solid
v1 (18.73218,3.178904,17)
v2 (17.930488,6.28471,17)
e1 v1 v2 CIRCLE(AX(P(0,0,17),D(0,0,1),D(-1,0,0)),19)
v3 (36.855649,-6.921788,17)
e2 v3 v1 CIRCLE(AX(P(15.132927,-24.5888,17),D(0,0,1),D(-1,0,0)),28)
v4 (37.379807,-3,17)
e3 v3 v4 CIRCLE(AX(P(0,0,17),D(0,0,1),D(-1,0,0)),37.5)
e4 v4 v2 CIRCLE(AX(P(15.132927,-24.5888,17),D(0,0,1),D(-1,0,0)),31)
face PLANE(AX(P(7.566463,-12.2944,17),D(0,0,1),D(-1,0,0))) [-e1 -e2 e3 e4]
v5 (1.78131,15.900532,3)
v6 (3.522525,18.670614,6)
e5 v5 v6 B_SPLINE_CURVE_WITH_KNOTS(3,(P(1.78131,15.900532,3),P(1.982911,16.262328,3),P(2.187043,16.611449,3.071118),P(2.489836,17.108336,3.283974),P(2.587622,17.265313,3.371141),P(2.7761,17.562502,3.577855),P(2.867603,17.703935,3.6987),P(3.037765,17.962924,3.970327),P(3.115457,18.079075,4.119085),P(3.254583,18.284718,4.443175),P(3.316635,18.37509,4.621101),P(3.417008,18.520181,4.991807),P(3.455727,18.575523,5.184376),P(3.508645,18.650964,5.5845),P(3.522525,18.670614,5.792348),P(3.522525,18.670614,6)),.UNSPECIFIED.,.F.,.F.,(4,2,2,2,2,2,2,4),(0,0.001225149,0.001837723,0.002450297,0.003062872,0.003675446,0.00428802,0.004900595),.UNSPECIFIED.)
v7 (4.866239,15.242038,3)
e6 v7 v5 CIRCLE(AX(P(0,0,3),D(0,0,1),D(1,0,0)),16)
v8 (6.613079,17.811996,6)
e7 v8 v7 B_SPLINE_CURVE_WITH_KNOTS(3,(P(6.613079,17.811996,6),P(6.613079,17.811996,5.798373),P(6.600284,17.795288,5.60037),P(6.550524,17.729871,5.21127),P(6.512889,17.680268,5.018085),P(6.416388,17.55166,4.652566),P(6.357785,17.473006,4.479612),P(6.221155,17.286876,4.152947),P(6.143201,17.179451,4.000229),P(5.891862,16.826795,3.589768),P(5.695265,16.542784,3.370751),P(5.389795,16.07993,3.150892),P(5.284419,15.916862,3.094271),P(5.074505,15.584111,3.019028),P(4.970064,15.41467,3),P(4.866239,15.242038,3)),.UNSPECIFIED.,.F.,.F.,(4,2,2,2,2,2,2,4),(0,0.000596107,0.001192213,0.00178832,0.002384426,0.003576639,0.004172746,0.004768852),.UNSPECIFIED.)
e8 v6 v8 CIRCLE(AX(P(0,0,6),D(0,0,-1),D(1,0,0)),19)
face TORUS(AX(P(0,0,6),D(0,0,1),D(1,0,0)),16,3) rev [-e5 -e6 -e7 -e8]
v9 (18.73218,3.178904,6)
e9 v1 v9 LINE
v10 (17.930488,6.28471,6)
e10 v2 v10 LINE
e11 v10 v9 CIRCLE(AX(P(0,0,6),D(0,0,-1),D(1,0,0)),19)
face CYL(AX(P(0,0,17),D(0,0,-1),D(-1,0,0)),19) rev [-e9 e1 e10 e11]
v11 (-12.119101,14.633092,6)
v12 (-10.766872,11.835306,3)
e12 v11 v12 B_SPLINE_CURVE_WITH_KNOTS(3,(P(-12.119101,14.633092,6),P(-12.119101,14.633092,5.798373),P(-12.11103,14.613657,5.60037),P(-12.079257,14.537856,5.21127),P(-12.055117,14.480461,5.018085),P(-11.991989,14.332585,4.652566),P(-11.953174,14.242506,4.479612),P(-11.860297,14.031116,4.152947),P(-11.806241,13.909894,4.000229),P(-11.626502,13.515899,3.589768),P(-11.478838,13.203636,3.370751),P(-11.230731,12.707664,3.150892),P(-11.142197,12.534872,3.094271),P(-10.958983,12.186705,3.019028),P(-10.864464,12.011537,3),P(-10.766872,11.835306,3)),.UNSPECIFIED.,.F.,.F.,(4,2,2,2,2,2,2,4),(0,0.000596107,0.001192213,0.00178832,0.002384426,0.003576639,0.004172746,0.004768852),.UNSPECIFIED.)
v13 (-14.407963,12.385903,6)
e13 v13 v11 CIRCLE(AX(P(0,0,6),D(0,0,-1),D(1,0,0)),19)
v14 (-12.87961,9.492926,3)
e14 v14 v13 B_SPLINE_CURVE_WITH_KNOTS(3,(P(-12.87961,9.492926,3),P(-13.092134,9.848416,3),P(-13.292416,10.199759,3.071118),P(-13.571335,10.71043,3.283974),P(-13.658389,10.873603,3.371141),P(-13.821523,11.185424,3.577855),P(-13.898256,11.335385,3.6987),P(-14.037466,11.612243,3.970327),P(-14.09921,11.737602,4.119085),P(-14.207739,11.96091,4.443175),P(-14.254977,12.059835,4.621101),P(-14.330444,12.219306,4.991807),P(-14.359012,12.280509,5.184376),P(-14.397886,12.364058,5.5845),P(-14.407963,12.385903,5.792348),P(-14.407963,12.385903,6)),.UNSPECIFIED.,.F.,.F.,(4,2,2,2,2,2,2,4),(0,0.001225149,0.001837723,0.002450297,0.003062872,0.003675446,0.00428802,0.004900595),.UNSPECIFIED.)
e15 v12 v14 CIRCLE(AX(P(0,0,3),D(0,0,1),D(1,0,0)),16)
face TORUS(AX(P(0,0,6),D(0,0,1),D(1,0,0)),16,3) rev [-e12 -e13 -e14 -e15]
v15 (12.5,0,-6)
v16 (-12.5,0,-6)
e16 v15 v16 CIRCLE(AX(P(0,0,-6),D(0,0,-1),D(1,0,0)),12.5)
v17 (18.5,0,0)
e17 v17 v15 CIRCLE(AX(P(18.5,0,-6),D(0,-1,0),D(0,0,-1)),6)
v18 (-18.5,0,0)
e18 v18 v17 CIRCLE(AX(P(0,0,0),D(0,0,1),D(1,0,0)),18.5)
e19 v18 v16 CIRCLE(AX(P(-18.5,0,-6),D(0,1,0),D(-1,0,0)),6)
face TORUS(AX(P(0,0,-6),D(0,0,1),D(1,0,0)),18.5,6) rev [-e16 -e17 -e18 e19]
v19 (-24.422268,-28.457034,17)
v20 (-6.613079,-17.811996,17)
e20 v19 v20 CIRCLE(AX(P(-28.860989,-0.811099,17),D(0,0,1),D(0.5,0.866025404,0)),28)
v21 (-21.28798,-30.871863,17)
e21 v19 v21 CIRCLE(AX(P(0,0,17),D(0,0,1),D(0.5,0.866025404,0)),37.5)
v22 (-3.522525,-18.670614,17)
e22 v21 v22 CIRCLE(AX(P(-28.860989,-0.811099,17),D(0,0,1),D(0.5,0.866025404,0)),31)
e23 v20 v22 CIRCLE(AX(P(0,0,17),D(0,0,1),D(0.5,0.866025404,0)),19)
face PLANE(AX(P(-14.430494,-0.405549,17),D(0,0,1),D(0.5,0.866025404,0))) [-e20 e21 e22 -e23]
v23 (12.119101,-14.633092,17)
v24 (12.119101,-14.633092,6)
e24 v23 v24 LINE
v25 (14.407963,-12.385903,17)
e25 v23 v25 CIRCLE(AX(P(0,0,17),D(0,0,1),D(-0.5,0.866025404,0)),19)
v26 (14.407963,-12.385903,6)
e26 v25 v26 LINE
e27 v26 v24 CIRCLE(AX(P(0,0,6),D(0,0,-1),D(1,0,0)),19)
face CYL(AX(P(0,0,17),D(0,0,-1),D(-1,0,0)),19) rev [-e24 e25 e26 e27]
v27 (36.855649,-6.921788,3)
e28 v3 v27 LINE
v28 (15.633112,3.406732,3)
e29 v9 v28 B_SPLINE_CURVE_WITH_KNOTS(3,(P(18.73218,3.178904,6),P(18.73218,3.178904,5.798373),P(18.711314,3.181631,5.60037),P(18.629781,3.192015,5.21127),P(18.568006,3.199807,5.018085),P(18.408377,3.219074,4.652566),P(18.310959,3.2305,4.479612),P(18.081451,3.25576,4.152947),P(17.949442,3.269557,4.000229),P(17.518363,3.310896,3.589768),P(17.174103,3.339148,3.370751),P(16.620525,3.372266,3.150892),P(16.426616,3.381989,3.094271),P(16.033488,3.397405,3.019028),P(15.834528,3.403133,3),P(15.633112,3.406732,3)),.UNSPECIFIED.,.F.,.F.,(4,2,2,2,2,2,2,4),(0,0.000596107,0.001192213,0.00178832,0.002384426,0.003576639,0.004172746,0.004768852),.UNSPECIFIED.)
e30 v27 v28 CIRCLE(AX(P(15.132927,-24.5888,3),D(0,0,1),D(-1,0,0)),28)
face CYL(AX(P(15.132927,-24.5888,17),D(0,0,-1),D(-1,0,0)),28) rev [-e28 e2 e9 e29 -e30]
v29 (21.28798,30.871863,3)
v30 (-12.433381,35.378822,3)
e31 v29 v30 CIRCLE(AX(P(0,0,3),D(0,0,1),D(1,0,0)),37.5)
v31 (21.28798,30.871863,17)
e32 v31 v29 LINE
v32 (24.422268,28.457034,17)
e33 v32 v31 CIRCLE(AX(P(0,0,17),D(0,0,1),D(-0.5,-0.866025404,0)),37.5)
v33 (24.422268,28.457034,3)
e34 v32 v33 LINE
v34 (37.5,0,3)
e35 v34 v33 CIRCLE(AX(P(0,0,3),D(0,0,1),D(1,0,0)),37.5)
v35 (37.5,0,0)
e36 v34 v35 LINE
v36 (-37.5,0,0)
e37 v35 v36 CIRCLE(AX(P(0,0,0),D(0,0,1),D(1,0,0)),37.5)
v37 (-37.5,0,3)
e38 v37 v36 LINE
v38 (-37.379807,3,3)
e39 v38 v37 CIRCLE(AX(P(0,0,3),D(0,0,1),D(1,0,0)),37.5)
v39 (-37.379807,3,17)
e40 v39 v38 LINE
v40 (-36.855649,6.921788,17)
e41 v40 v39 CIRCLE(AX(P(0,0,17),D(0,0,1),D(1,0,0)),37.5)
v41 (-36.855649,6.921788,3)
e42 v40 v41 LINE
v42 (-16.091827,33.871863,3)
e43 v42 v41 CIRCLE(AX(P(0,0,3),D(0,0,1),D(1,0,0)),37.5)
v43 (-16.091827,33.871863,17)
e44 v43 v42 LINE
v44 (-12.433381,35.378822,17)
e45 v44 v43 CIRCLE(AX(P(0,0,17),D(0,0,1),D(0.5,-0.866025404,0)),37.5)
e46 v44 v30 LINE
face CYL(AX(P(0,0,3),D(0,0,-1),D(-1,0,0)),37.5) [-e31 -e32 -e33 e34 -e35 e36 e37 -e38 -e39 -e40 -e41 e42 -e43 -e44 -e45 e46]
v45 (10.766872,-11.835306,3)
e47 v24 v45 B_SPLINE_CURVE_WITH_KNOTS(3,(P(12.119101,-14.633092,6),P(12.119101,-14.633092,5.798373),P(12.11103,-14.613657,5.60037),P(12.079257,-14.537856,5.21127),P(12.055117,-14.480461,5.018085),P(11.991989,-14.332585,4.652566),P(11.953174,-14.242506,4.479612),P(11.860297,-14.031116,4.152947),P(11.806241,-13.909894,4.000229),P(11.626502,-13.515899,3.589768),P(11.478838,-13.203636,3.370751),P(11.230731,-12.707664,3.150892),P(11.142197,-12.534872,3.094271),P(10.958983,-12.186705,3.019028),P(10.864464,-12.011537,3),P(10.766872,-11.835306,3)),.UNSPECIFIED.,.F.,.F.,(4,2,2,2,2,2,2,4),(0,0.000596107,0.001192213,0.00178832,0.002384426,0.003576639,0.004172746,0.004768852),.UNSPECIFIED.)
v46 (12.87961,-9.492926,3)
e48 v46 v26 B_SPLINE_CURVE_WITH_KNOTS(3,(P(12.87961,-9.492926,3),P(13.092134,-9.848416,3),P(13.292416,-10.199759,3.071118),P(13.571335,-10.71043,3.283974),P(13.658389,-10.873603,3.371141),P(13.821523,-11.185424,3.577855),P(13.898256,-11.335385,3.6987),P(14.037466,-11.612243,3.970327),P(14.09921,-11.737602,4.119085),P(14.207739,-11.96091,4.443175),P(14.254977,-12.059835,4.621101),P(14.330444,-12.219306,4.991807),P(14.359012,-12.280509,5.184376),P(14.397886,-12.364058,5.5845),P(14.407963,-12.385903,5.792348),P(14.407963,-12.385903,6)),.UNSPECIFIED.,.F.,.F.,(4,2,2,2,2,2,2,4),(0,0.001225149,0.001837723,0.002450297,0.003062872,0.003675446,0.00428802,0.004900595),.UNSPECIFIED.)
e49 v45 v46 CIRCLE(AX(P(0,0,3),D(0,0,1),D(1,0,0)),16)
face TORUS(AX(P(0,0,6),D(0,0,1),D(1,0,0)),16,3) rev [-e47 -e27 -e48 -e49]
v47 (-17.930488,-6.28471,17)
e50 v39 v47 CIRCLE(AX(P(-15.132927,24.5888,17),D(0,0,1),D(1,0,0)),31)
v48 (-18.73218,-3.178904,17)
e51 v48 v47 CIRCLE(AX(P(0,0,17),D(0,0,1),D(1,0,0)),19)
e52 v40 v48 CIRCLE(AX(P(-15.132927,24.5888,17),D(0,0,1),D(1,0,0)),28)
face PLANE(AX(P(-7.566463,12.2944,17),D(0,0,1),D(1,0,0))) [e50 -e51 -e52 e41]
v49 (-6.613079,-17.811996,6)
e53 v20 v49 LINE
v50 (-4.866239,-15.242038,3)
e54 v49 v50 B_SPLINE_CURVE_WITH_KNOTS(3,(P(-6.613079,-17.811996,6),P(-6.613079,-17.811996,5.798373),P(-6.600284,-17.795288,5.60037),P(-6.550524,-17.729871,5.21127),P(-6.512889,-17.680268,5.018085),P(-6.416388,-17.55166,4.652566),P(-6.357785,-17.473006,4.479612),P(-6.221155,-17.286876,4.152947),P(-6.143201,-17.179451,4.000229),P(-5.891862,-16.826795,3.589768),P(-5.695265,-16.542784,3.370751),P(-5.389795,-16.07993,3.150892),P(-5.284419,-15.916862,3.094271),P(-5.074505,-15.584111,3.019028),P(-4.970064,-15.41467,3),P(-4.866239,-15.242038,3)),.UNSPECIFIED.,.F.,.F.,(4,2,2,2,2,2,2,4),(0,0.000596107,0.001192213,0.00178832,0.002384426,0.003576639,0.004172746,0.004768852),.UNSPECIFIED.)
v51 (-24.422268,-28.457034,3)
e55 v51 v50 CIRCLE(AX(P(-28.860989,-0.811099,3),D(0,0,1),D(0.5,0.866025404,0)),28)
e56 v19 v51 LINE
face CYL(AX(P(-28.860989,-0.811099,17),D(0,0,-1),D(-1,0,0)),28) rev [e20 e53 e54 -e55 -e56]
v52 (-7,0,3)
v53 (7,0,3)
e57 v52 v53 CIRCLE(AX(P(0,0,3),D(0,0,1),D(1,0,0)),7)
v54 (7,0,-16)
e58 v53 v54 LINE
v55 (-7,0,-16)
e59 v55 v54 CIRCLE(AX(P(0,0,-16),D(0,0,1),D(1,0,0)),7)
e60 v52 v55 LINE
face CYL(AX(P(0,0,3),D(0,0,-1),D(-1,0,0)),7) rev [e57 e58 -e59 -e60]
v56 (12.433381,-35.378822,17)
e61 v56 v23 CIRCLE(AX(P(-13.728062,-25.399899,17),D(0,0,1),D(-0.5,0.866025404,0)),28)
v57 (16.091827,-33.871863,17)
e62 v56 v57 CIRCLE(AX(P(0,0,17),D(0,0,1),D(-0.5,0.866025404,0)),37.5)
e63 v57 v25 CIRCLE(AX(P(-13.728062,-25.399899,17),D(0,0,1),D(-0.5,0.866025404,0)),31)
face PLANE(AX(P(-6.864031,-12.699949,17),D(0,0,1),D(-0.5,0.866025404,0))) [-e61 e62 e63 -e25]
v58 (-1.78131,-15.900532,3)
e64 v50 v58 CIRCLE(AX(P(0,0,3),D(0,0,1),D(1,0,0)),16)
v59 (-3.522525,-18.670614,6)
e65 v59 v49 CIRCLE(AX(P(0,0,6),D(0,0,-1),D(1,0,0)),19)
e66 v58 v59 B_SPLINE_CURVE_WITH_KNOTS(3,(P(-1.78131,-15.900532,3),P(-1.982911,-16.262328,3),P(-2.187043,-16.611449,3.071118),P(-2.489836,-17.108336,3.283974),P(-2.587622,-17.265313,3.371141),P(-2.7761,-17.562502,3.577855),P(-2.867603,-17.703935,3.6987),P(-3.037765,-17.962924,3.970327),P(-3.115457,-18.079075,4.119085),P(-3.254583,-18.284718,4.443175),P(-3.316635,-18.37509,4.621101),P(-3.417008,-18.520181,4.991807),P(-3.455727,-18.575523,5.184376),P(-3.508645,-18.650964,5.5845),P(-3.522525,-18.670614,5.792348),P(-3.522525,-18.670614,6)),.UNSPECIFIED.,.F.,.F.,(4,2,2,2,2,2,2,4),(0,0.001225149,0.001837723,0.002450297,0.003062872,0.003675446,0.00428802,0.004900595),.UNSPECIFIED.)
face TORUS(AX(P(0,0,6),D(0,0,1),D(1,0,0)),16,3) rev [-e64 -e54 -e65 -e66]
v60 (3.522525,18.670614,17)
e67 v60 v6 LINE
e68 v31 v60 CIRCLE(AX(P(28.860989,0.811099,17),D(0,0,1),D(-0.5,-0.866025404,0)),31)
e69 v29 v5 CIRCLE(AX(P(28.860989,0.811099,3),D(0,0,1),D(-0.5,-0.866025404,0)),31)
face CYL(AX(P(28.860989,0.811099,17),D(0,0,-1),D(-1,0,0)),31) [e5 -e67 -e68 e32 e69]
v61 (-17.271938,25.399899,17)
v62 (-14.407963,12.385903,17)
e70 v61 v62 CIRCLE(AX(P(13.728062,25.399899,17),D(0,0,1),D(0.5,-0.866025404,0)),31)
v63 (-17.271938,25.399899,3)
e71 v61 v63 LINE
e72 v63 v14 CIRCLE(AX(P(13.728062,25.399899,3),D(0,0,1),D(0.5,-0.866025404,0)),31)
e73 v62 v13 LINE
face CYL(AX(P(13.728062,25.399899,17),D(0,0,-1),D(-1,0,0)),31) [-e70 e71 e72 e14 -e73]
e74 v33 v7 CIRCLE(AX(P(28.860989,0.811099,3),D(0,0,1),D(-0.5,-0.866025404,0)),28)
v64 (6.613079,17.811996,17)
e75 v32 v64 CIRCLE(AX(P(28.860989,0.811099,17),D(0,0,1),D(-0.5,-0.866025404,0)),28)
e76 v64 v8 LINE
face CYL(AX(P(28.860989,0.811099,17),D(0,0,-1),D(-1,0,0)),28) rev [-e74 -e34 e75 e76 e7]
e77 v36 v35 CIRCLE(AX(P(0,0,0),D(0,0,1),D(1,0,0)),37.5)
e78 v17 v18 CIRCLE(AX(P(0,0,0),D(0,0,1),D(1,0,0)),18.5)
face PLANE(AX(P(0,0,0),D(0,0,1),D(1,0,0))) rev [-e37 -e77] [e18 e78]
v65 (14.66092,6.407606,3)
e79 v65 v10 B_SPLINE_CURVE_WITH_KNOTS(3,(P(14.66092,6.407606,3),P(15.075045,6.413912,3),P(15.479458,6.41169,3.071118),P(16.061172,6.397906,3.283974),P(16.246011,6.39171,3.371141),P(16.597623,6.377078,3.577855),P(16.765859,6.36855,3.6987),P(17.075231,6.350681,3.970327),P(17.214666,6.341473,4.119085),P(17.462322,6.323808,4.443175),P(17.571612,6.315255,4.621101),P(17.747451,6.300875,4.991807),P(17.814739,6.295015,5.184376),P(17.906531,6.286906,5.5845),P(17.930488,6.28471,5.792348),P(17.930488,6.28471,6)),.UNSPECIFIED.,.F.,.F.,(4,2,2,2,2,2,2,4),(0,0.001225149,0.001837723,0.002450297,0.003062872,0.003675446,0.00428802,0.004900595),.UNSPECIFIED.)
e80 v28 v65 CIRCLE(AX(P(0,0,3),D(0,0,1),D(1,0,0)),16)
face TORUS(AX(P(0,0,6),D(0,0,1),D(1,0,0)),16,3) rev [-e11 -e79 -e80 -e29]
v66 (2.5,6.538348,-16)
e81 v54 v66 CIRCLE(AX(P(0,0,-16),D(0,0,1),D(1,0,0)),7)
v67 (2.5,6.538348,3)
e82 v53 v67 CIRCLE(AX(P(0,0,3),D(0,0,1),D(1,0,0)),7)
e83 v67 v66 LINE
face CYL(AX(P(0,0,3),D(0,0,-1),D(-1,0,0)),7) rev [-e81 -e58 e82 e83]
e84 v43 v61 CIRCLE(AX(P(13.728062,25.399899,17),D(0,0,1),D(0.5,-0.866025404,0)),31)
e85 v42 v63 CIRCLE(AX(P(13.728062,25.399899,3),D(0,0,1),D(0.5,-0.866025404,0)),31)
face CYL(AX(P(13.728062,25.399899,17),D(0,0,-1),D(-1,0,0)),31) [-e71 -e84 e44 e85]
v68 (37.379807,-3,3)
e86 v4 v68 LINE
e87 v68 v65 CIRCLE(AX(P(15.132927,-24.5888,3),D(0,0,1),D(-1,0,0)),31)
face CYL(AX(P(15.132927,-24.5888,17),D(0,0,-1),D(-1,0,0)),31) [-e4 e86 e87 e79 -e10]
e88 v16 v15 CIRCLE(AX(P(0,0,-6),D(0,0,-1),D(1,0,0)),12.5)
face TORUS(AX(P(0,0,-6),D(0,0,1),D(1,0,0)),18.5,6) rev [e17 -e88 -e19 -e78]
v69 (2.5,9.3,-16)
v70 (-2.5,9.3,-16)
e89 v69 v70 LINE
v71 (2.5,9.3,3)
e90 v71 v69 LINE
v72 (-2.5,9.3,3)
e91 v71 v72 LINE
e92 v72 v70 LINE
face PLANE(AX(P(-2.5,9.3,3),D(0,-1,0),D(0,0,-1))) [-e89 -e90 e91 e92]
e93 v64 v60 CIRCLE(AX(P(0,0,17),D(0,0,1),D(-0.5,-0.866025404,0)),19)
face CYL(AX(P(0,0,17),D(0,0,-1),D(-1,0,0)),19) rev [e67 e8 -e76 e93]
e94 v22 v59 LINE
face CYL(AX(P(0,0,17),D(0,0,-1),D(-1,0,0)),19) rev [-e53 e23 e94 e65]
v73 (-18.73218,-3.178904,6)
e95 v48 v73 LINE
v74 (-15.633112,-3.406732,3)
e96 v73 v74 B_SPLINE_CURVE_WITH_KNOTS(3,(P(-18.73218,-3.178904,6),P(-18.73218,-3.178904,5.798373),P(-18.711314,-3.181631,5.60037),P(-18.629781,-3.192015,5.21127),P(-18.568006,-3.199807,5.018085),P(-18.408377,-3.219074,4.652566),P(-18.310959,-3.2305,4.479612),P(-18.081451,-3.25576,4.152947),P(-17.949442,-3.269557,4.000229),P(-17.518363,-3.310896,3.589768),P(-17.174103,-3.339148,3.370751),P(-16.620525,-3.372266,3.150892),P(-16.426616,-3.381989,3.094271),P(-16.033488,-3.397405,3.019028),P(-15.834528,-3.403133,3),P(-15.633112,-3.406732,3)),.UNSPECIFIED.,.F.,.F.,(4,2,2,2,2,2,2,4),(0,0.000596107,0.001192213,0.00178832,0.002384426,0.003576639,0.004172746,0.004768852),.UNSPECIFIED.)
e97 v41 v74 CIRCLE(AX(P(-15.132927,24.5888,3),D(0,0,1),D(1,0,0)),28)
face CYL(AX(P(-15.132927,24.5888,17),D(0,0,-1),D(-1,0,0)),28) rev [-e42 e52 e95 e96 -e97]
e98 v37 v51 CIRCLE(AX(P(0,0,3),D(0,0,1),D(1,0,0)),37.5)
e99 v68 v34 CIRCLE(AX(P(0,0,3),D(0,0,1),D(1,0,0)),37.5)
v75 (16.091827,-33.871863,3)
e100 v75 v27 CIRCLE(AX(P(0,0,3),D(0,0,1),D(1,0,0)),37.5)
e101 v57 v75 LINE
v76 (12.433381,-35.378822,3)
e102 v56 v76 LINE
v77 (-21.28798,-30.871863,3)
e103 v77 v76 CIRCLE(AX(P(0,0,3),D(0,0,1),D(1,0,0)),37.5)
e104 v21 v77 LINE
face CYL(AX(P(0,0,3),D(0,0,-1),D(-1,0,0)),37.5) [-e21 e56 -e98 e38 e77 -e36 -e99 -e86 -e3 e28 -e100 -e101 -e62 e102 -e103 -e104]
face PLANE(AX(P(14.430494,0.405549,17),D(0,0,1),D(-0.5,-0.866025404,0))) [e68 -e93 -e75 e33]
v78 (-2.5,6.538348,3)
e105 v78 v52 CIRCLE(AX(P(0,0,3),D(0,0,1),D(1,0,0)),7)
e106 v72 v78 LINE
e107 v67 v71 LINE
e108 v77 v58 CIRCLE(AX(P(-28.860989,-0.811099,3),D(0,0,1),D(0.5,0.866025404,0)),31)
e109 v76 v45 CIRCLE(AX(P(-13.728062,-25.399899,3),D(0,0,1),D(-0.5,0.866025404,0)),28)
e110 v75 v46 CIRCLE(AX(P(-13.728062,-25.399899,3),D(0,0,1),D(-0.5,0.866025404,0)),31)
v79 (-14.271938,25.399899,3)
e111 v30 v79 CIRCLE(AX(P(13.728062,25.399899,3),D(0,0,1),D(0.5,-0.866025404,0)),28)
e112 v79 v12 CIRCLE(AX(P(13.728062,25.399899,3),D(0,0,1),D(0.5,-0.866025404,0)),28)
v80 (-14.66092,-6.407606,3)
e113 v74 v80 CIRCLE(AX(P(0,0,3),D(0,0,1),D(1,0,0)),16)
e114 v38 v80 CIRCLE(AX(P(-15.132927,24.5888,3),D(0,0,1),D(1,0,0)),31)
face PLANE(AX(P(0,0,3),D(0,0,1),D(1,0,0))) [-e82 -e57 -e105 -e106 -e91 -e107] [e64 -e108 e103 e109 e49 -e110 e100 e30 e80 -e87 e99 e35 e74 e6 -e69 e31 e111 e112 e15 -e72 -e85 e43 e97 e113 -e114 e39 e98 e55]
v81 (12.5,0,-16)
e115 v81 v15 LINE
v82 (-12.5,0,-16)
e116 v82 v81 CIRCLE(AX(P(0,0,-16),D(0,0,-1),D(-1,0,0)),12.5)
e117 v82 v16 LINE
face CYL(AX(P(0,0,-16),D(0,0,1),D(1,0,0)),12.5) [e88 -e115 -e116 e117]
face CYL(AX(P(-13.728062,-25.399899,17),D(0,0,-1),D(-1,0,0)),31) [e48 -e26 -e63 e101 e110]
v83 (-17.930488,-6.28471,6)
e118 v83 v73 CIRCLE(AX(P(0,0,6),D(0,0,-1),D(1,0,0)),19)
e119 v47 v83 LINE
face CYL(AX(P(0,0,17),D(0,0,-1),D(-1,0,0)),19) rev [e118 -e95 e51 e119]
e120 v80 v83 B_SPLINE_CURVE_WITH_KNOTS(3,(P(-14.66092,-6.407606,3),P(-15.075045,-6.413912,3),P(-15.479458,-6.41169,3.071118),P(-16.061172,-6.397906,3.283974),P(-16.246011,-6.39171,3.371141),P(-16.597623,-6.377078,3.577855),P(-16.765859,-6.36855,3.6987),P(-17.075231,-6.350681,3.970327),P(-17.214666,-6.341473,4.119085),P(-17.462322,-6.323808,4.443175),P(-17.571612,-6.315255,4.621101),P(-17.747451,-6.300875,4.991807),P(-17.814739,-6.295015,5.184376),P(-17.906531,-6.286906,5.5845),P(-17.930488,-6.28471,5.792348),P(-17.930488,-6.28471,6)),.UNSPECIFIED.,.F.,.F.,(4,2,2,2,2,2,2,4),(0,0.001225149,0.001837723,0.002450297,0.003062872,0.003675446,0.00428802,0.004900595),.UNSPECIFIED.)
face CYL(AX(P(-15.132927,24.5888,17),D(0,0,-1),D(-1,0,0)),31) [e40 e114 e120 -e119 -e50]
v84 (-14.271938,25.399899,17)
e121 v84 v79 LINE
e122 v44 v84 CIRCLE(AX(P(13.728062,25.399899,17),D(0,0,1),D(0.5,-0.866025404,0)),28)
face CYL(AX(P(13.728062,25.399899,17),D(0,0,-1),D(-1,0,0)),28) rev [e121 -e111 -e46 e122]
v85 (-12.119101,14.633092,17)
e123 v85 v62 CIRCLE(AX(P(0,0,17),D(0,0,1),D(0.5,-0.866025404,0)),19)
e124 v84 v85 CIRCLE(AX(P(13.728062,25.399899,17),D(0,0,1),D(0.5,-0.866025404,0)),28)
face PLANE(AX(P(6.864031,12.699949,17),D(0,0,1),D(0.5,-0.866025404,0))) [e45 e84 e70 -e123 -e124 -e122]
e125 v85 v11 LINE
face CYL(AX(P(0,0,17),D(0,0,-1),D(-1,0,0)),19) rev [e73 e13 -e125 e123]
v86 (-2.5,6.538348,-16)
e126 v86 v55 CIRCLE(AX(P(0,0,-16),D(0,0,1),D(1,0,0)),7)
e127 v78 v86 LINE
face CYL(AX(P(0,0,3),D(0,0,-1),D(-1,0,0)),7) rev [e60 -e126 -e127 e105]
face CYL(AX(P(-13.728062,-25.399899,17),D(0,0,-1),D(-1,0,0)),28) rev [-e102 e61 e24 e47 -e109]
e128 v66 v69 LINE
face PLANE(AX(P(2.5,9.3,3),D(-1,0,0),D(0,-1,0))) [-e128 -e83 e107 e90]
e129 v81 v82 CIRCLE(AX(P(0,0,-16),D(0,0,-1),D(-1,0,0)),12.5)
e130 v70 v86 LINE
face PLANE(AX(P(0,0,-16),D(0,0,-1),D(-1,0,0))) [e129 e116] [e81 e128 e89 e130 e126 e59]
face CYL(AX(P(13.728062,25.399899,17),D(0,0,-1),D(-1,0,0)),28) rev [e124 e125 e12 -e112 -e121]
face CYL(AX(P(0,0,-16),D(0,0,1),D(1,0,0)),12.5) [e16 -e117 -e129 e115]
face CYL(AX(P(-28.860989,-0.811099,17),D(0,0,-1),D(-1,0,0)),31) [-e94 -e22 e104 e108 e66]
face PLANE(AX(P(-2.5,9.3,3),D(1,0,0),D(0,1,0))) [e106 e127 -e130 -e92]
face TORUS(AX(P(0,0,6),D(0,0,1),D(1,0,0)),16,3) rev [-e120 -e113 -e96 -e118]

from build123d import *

# Parameters (mm, degrees)
BACK_DISC_SKETCH_R    = 37.5
BACK_DISC_75_DEPTH    = 3
HUB_SKETCH_R          = 12.5
HUB_25_DEPTH          = 16
SHAFT_START           = -16
SHAFT_BORE_DEPTH      = 16
HUB_ROOT_FILLET_R6_R  = 6
VANE_DEPTH            = 14
VANE_PATTERN_6X_COUNT = 6
VANE_FILLETS_R3_R     = 3


with BuildPart() as part:
    # Back Disc Sketch → Back Disc Ø75 (new body)
    with BuildSketch(Plane.XY):
        Circle(BACK_DISC_SKETCH_R)
        with BuildLine():
            Line((-2.5, 9.3), (2.5, 9.3))
            Line((2.5, 9.3), (2.5, 6.538348415))
            ThreePointArc((2.5, 6.538348415), (0, -7), (-2.5, 6.538348415))
            Line((-2.5, 6.538348415), (-2.5, 9.3))
        make_face(mode=Mode.SUBTRACT)
    extrude(amount=BACK_DISC_75_DEPTH)

    # Hub Sketch → Hub Ø25 (add)
    with BuildSketch(Plane(origin=(0, 0, 0), x_dir=(-1, 0, 0), z_dir=(0, 0, -1))):
        with Locations(Location((0, 0, 0), (0, 0, 180))):
            Circle(HUB_SKETCH_R)
    extrude(amount=HUB_25_DEPTH)

    # Shaft Bore Sketch → Shaft Bore (cut)
    with BuildSketch(Plane.XY.offset(SHAFT_START)):
        with BuildLine():
            Line((-2.5, 9.3), (-2.5, 6.538348415))
            ThreePointArc((-2.5, 6.538348415), (0, -7), (2.5, 6.538348415))
            Line((2.5, 6.538348415), (2.5, 9.3))
            Line((2.5, 9.3), (-2.5, 9.3))
        make_face()
    extrude(amount=SHAFT_BORE_DEPTH, mode=Mode.SUBTRACT)

    # Hub Root Fillet R6
    hub_root_fillet_r6_edges = [part.edges().sort_by_distance(p)[0] for p in [
        (-12.5, 0, 0),
    ]]
    fillet(hub_root_fillet_r6_edges, radius=HUB_ROOT_FILLET_R6_R)

    # Vane Sketch → Vane (add)
    with BuildSketch(Plane.XY.offset(3)):
        with BuildLine():
            ThreePointArc((-36.855648906, 6.92178761), (-28.764016269, 0.130807743), (-18.732180108, -3.178903649))
            ThreePointArc((-18.732180108, -3.178903649), (-18.396992291, -4.748755064), (-17.930488458, -6.284710307))
            ThreePointArc((-17.930488458, -6.284710307), (-28.487981374, -3.38694846), (-37.379807383, 3))
            ThreePointArc((-37.379807383, 3), (-37.16948812, 4.967811678), (-36.855648906, 6.92178761))
        make_face()
    vane = extrude(amount=VANE_DEPTH)

    # Vane Pattern 6x: Vane ×6 about axis
    vane_pattern_6x_axis = Axis((0, 0, 0), (0, 0, 1))
    for i in range(1, VANE_PATTERN_6X_COUNT):
        add(vane.rotate(vane_pattern_6x_axis, i * 360 / VANE_PATTERN_6X_COUNT))

    # Vane Fillets R3
    vane_fillets_r3_edges = [part.edges().sort_by_distance(p)[0] for p in [
        (-13.311038667, 13.557885145, 3),
        (-18.396992291, -4.748755064, 3),
        (-5.085953624, -18.306640209, 3),
        (13.311038667, -13.557885145, 3),
        (18.396992291, 4.748755064, 3),
        (5.085953624, 18.306640209, 3),
    ]]
    fillet(vane_fillets_r3_edges, radius=VANE_FILLETS_R3_R)


solid = part.part
